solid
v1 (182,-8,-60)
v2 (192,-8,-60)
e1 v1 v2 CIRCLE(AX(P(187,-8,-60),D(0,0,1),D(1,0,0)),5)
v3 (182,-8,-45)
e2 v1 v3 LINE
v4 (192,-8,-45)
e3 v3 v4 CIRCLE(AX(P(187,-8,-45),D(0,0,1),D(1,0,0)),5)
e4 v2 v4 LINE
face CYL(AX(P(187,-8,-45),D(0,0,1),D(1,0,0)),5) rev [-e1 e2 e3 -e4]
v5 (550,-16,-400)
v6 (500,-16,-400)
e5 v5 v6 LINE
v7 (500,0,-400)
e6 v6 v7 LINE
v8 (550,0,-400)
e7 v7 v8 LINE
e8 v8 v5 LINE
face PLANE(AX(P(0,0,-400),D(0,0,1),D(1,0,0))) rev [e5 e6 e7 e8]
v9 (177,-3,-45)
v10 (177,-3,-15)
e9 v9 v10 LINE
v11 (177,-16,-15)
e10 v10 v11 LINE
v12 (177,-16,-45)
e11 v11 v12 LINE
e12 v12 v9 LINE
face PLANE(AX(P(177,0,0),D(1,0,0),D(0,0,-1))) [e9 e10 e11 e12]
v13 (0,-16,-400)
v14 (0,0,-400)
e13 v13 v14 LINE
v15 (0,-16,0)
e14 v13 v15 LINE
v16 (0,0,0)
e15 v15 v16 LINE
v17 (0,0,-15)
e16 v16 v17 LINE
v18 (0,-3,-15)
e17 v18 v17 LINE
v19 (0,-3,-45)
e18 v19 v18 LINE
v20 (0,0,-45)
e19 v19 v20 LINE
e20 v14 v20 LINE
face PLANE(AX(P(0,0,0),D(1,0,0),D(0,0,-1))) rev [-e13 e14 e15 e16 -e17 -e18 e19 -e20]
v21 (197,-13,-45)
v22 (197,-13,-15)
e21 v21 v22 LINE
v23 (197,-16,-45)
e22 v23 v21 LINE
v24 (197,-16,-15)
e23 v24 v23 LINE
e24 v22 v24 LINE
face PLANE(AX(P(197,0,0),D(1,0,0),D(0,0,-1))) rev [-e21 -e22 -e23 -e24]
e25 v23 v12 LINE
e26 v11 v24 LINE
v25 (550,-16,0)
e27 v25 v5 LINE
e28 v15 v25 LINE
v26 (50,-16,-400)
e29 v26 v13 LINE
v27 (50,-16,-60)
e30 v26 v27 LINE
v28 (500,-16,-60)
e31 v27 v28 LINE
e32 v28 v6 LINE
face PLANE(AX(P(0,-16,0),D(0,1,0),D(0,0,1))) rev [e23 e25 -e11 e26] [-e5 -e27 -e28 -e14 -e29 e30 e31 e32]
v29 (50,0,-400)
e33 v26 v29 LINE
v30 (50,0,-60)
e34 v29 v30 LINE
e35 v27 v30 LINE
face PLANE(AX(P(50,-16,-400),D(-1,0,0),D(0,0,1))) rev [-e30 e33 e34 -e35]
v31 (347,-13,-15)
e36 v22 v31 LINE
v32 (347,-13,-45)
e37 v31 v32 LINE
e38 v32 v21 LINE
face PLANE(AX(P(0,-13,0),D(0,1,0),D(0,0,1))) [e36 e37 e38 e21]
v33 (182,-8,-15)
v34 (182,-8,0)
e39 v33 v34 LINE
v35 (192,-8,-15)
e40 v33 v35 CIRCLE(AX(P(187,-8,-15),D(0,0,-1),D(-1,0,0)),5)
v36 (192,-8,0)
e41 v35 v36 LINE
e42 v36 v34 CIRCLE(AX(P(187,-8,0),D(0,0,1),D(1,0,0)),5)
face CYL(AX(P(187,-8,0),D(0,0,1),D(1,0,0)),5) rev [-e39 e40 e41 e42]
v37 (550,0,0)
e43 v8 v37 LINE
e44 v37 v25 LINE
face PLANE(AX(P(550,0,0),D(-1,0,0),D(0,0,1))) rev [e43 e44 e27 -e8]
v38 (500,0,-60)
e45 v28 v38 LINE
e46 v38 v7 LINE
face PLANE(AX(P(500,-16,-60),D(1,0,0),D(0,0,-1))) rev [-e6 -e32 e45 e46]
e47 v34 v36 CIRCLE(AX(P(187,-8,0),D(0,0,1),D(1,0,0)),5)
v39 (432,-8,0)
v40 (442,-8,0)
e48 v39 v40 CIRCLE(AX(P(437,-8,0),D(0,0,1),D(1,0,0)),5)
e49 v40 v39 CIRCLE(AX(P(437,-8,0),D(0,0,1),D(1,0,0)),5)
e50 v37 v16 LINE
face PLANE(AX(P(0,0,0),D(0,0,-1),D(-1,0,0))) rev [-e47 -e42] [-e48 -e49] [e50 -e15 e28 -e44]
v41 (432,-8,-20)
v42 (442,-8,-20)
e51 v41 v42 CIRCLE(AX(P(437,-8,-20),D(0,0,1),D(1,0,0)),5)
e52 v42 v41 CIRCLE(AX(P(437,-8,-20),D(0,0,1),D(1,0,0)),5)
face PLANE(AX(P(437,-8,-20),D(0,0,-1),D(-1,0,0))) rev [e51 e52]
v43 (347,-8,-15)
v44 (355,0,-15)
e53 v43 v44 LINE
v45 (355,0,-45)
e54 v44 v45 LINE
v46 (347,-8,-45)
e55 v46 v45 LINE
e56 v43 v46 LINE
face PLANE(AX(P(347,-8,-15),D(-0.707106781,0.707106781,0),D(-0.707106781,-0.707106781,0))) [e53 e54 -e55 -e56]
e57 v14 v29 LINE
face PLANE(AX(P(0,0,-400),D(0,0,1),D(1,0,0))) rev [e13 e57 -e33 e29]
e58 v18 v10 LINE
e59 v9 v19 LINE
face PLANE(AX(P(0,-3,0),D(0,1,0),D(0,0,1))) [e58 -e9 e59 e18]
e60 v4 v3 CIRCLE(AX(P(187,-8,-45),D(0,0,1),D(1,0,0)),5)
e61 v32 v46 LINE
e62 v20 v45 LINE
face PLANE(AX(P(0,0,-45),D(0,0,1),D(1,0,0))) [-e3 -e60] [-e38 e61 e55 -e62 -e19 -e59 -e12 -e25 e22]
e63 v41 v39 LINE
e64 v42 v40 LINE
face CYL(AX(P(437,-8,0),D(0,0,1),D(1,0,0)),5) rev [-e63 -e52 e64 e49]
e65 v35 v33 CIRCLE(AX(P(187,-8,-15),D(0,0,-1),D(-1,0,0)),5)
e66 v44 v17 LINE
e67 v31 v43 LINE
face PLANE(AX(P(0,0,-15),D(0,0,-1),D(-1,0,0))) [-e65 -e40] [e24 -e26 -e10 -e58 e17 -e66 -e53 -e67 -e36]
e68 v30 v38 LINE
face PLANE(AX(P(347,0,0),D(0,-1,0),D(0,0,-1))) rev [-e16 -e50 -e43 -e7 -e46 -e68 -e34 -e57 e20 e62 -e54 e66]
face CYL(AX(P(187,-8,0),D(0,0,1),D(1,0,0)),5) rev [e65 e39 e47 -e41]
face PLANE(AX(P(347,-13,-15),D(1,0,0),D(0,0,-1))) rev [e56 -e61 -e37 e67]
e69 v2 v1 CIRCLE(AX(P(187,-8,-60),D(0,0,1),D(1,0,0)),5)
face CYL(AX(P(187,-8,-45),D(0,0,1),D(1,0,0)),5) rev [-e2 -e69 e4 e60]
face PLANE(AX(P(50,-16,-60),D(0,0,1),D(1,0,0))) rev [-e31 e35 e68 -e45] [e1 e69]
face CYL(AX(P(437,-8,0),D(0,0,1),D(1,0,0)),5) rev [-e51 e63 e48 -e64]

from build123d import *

# Parameters (mm, degrees)
BOSS_EXTRUDE1_DEPTH            = 30
SKETCH2_W                      = 8
SKETCH2_H                      = 30
BOSS_EXTRUDE2_DEPTH            = 8
SKETCH3_W                      = 8
SKETCH3_H                      = 16
BOSS_EXTRUDE3_DEPTH            = 15
SKETCH4_W                      = 45
SKETCH4_H                      = 16
BOSS_EXTRUDE4_DEPTH            = 195
SKETCH5_W                      = 45
SKETCH5_H                      = 16
BOSS_EXTRUDE5_DEPTH            = 347
SKETCH6_W                      = 347
SKETCH6_H                      = 30
CUT_EXTRUDE1_DEPTH             = 3
SKETCH7_W                      = 30
SKETCH7_H                      = 5
CUT_EXTRUDE2_DEPTH             = 150
SKETCH8_W                      = 30
SKETCH8_H                      = 13
CUT_EXTRUDE3_DEPTH             = 20
SKETCH9_W                      = 150
SKETCH9_H                      = 30
CUT_EXTRUDE4_DEPTH             = 5
SKETCH10_W                     = 550
SKETCH10_H                     = 16
BOSS_EXTRUDE6_DEPTH            = 355
SKETCH11_W                     = 450
SKETCH11_H                     = 340
CUT_EXTRUDE5_DEPTH             = 681.261714342
F_10_0_10_DIAMETER_HOLE1_D     = 10
F_10_0_10_DIAMETER_HOLE1_DEPTH = 20
F_10_0_10_DIAMETER_HOLE2_D     = 10
F_10_0_10_DIAMETER_HOLE2_DEPTH = 15
F_10_0_10_DIAMETER_HOLE3_D     = 10
F_10_0_10_DIAMETER_HOLE3_DEPTH = 355


with BuildPart() as part:
    # Sketch1 → Boss-Extrude1 (new body)
    with BuildSketch(Plane(origin=(0, 0, -45), x_dir=(-1, 0, 0), z_dir=(0, 0, -1))):
        Polygon((-355, -8), (-347, -8), (-355, 0), align=None)
    extrude(amount=-BOSS_EXTRUDE1_DEPTH)

    # Sketch2 → Boss-Extrude2 (add)
    with BuildSketch(Plane.XZ.offset(8)):
        with Locations((351, -30)):
            Rectangle(SKETCH2_W, SKETCH2_H)
    extrude(amount=BOSS_EXTRUDE2_DEPTH)

    # Sketch3 → Boss-Extrude3 (add)
    with BuildSketch(Plane.XY.offset(-15)):
        with Locations((351, -8)):
            Rectangle(SKETCH3_W, SKETCH3_H)
    extrude(amount=BOSS_EXTRUDE3_DEPTH)

    # Sketch4 → Boss-Extrude4 (add)
    with BuildSketch(Plane(origin=(355, 0, 0), x_dir=(0, 0, -1), z_dir=(1, 0, 0))):
        with Locations((22.5, -8)):
            Rectangle(SKETCH4_W, SKETCH4_H)
    extrude(amount=BOSS_EXTRUDE4_DEPTH)

    # Sketch5 → Boss-Extrude5 (add)
    with BuildSketch(Plane.ZY.offset(-347)):
        with Locations((-22.5, -8)):
            Rectangle(SKETCH5_W, SKETCH5_H)
    extrude(amount=BOSS_EXTRUDE5_DEPTH)

    # Sketch6 → Cut-Extrude1 (cut)
    with BuildSketch(Plane(origin=(0, 0, 0), x_dir=(-1, 0, 0), z_dir=(0, 1, 0))):
        with Locations((-173.5, -30)):
            Rectangle(SKETCH6_W, SKETCH6_H)
    extrude(amount=-CUT_EXTRUDE1_DEPTH, mode=Mode.SUBTRACT)

    # Sketch7 → Cut-Extrude2 (cut)
    with BuildSketch(Plane(origin=(347, 0, 0), x_dir=(0, 0, -1), z_dir=(1, 0, 0))):
        with Locations((30, -5.5)):
            Rectangle(SKETCH7_W, SKETCH7_H)
    extrude(amount=-CUT_EXTRUDE2_DEPTH, mode=Mode.SUBTRACT)

    # Sketch8 → Cut-Extrude3 (cut)
    with BuildSketch(Plane(origin=(197, 0, 0), x_dir=(0, 0, -1), z_dir=(1, 0, 0))):
        with Locations((30, -9.5)):
            Rectangle(SKETCH8_W, SKETCH8_H)
    extrude(amount=-CUT_EXTRUDE3_DEPTH, mode=Mode.SUBTRACT)

    # Sketch9 → Cut-Extrude4 (cut)
    with BuildSketch(Plane(origin=(0, -8, 0), x_dir=(-1, 0, 0), z_dir=(0, 1, 0))):
        with Locations((-272, -30)):
            Rectangle(SKETCH9_W, SKETCH9_H)
    extrude(amount=-CUT_EXTRUDE4_DEPTH, mode=Mode.SUBTRACT)

    # Sketch10 → Boss-Extrude6 (add)
    with BuildSketch(Plane(origin=(0, 0, -45), x_dir=(-1, 0, 0), z_dir=(0, 0, -1))):
        with Locations((-275, -8)):
            Rectangle(SKETCH10_W, SKETCH10_H)
    extrude(amount=BOSS_EXTRUDE6_DEPTH)

    # Sketch11 → Cut-Extrude5 (cut, through all)
    with BuildSketch(Plane(origin=(0, 0, 0), x_dir=(-1, 0, 0), z_dir=(0, 1, 0))):
        with Locations((-275, -230)):
            Rectangle(SKETCH11_W, SKETCH11_H)
    extrude(amount=-CUT_EXTRUDE5_DEPTH, mode=Mode.SUBTRACT)

    # Ø10.0 (10) Diameter Hole1
    with Locations(Plane.XY):
        with Locations((437, -8)):
            Hole(F_10_0_10_DIAMETER_HOLE1_D / 2, depth=F_10_0_10_DIAMETER_HOLE1_DEPTH)

    # Ø10.0 (10) Diameter Hole2
    with Locations(Plane.XY):
        with Locations((187, -8)):
            Hole(F_10_0_10_DIAMETER_HOLE2_D / 2, depth=F_10_0_10_DIAMETER_HOLE2_DEPTH)

    # Ø10.0 (10) Diameter Hole3
    with Locations(Plane.XY.offset(-45)):
        with Locations((187, -8)):
            Hole(F_10_0_10_DIAMETER_HOLE3_D / 2, depth=F_10_0_10_DIAMETER_HOLE3_DEPTH)


solid = part.part
